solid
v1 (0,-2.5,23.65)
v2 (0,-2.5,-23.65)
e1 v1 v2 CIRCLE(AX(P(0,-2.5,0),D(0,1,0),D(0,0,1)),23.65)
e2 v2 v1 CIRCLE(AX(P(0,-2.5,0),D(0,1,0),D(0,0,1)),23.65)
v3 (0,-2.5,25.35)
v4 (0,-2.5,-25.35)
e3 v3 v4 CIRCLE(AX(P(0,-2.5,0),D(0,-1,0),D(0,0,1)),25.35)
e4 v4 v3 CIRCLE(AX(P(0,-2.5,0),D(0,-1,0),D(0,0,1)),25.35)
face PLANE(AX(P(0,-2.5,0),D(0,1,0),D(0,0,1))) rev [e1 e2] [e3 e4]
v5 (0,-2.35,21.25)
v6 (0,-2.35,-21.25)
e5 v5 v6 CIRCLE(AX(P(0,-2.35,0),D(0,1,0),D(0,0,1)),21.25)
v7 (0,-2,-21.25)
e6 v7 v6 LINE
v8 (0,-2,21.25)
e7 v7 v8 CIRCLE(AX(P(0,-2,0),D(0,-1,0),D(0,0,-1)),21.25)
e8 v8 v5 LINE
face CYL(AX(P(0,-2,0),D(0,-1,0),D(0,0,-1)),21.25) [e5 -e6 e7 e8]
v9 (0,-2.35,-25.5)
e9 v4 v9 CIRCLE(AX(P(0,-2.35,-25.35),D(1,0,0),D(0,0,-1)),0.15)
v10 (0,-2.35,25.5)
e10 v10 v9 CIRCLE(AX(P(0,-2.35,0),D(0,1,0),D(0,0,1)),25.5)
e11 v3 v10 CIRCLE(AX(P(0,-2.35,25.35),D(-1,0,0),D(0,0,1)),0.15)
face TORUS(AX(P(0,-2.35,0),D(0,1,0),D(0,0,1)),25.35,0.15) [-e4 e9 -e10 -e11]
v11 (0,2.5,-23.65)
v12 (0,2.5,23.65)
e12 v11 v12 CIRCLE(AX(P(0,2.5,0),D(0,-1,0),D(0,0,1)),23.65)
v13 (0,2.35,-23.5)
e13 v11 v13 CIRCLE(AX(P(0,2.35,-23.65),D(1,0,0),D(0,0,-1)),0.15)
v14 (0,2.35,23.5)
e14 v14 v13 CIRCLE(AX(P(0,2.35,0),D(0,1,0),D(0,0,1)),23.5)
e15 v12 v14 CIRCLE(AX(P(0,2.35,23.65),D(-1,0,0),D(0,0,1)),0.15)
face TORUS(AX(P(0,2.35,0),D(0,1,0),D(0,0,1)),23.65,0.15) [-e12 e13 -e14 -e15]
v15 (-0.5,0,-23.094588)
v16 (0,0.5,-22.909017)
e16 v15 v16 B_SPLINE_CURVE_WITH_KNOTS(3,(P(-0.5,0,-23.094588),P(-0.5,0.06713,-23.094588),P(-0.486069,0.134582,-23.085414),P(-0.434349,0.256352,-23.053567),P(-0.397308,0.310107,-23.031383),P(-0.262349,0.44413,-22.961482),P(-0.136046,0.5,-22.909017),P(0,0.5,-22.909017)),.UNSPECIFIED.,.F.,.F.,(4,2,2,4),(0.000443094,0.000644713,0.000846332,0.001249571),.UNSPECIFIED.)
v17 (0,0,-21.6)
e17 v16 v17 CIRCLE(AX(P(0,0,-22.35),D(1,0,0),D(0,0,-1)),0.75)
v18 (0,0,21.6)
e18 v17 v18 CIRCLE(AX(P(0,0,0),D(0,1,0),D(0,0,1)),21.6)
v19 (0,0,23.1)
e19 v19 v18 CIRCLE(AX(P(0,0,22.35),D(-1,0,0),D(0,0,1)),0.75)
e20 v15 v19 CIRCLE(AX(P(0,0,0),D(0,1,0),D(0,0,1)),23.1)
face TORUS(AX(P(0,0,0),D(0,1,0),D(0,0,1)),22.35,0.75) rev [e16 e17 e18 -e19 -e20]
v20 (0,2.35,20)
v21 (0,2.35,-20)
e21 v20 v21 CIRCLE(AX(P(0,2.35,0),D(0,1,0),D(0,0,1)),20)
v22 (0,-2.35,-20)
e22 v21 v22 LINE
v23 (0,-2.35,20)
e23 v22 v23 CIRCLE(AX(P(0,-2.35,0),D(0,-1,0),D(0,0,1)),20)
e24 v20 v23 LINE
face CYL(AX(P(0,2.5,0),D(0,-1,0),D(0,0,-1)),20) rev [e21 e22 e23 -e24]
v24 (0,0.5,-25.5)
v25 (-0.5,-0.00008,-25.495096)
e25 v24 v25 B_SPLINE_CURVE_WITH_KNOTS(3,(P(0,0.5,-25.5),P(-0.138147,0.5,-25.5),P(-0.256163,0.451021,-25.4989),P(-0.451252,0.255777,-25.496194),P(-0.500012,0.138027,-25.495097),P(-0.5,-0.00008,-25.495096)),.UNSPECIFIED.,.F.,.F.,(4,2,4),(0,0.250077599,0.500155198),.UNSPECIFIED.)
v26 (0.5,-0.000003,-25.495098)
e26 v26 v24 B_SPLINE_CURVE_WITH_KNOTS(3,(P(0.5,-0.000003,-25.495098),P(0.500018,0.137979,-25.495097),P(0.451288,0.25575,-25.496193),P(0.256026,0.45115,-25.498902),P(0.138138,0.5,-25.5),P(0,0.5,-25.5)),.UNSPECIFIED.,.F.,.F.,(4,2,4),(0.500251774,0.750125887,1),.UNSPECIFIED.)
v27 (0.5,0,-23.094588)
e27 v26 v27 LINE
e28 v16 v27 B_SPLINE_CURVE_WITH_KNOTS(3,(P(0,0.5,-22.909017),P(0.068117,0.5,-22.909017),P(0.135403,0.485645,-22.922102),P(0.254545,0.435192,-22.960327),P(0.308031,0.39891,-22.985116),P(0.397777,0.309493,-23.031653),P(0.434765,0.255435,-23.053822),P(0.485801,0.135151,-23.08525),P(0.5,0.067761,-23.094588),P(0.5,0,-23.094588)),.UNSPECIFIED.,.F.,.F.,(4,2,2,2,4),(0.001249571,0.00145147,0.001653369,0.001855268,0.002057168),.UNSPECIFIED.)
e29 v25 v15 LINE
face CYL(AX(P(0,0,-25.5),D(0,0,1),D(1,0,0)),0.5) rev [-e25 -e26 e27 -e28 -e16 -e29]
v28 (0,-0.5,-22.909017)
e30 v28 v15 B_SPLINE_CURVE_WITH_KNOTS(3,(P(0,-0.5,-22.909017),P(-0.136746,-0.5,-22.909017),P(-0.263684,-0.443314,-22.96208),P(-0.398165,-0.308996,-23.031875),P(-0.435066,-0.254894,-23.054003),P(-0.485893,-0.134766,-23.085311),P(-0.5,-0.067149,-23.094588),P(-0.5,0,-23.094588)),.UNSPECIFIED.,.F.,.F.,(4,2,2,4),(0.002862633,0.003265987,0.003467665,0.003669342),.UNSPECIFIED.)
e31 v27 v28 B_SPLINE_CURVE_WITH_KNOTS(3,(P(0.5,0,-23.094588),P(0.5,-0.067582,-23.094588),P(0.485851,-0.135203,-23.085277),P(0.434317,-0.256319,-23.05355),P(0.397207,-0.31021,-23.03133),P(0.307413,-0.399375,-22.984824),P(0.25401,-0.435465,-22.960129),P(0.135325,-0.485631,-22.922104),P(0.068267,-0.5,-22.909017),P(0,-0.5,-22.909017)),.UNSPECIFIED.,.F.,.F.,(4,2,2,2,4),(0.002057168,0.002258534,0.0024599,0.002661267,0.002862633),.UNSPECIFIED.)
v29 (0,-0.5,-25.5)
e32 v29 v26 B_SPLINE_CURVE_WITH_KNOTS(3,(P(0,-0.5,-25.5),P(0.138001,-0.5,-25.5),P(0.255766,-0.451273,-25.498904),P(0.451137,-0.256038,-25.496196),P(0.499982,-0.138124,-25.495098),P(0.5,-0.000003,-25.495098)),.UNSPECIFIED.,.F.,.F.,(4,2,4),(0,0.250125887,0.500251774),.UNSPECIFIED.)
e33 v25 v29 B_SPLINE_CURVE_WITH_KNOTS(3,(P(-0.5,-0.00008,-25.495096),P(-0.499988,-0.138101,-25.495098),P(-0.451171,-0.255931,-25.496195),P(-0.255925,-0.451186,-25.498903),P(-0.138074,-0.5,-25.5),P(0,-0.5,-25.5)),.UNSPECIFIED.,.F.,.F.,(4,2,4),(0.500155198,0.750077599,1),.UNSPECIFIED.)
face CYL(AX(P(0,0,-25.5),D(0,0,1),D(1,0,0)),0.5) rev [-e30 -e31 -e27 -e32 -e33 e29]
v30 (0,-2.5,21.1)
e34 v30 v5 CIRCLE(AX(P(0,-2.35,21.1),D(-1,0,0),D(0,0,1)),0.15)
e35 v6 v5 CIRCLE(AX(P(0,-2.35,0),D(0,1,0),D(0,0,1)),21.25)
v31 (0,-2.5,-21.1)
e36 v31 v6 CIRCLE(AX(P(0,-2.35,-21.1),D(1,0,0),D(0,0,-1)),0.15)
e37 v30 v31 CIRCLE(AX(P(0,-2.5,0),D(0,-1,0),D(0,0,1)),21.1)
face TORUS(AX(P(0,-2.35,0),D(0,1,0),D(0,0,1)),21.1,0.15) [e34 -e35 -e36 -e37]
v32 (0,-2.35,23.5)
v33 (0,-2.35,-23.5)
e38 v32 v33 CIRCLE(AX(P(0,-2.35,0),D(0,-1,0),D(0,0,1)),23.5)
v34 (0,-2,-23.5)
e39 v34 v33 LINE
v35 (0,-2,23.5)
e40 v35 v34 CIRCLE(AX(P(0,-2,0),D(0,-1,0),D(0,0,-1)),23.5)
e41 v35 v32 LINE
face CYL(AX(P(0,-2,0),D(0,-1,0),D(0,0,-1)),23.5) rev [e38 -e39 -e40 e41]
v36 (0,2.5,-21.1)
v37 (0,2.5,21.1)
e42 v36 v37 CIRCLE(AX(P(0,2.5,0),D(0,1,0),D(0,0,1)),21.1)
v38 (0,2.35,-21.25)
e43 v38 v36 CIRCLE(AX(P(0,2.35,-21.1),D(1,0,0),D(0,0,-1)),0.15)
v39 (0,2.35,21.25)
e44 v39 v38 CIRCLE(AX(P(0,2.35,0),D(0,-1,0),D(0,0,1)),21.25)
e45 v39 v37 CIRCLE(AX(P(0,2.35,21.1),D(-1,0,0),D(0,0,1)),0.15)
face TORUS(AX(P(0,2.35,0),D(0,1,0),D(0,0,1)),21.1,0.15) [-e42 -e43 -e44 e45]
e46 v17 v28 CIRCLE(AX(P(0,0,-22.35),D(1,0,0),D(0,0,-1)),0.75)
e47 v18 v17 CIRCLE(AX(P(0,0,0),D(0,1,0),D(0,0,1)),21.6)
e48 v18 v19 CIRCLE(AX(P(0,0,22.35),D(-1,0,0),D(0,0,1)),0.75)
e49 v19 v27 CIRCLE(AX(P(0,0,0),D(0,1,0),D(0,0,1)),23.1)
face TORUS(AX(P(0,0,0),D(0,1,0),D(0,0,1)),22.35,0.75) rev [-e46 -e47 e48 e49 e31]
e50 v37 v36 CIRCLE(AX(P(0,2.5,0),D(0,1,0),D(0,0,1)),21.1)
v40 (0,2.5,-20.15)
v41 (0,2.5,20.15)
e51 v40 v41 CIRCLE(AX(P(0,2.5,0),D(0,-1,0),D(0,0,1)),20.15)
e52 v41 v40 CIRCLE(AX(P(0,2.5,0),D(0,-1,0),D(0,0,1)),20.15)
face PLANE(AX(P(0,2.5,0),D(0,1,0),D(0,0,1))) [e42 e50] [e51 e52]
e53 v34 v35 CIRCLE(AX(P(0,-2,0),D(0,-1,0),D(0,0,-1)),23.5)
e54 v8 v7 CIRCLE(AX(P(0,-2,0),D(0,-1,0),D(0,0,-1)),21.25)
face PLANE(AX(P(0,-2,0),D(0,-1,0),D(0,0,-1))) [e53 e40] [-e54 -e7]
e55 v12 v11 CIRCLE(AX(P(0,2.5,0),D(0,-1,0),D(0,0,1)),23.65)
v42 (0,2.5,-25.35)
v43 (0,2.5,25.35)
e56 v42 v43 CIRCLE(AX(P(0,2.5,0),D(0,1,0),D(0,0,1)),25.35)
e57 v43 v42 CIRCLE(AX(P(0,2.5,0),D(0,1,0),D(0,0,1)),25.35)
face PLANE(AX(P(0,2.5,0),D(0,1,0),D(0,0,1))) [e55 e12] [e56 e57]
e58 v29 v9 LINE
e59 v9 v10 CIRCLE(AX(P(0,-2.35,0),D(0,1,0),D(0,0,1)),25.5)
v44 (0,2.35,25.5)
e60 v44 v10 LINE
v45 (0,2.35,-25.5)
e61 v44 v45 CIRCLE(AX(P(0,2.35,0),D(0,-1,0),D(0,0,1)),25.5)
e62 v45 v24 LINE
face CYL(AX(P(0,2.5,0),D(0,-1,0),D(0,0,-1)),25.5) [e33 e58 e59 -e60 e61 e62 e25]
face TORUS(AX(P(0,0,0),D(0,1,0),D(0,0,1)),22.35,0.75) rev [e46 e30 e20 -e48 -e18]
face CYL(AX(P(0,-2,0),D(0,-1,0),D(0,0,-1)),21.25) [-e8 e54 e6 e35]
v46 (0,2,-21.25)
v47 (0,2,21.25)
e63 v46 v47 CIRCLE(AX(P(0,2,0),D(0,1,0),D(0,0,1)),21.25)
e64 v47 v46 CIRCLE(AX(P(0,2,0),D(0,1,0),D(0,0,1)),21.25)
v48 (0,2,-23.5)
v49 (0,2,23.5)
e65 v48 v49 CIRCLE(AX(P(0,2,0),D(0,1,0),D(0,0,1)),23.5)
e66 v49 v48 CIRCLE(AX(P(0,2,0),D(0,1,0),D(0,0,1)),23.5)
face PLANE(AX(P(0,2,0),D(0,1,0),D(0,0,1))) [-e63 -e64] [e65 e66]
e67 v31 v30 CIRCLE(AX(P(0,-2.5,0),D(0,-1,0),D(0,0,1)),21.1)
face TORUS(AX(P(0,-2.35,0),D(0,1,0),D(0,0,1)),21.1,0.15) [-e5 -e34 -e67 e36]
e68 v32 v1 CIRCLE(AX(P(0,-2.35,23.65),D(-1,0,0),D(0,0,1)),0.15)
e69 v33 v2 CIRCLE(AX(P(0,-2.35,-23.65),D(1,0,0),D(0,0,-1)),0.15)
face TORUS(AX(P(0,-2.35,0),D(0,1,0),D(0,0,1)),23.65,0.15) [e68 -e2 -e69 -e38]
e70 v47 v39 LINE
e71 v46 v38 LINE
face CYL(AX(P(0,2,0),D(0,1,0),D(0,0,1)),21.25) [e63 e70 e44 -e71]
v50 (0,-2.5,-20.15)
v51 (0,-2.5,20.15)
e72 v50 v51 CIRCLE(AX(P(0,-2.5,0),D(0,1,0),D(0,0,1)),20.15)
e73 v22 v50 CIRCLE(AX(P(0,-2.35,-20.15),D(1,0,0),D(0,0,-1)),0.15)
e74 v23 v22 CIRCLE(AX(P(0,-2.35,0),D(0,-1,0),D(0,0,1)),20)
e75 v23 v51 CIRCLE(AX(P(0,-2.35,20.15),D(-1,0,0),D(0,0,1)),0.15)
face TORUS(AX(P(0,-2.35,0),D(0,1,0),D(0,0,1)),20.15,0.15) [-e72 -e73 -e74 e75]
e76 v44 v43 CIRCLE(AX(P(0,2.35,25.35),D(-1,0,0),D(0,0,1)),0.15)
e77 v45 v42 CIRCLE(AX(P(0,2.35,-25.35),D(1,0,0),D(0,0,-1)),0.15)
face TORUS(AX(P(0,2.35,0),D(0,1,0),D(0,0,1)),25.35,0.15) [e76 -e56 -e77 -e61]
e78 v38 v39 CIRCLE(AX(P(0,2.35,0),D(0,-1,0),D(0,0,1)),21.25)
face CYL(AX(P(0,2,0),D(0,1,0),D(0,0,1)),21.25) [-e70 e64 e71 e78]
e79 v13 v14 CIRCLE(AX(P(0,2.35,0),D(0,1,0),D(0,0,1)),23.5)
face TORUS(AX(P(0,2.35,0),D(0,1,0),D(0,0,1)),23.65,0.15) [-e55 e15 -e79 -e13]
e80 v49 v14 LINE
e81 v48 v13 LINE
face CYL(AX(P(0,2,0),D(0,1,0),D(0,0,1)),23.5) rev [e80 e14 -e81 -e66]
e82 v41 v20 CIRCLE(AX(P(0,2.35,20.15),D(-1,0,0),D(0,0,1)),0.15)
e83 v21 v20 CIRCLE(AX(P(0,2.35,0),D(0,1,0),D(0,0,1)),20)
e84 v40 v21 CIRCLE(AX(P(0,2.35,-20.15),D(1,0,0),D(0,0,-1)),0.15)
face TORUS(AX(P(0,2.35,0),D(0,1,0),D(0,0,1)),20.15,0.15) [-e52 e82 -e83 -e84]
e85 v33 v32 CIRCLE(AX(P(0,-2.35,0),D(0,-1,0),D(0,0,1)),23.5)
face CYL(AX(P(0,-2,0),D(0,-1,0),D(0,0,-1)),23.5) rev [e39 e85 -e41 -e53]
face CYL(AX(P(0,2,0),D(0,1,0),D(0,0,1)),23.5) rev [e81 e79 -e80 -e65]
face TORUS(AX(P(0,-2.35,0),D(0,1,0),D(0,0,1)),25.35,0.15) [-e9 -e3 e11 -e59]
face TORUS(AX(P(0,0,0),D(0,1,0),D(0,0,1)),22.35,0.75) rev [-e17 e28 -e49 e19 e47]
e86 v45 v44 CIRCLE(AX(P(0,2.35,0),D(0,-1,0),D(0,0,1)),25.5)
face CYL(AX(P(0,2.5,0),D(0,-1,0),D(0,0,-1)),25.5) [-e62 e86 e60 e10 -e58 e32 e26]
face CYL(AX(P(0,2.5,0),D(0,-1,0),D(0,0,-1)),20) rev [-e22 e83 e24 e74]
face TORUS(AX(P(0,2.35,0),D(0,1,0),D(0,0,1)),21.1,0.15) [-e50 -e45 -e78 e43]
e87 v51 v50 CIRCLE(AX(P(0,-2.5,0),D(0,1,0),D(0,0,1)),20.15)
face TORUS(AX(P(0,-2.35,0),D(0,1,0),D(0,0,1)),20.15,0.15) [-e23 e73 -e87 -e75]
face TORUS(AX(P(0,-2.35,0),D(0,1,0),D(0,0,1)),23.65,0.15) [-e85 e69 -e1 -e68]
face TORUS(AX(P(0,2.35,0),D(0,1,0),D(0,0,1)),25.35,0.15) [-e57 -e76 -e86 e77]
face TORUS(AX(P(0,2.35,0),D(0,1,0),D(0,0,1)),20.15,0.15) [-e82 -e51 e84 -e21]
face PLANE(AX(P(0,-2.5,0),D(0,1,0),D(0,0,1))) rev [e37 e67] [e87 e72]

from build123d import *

# Parameters (mm, degrees)
SKETCH_1_R            = 25.5
SKETCH_1_R_2          = 20
EXTRUDE_1_DEPTH       = 2.5
SKETCH_2_R            = 23.5
SKETCH_2_R_2          = 21.25
CUT_EXTRUDE_433_DEPTH = 0.5
CUT_EXTRUDE_START     = -0.5
SKETCH_3_R            = 23.5
SKETCH_3_R_2          = 21.25
CUT_EXTRUDE_567_DEPTH = 0.5
SKETCH_4_R            = 0.75
CUT_EXTRUDE_START_2   = -22.35
SKETCH_5_R            = 0.5
CUT_EXTRUDE_1_DEPTH   = 14.79899722
FILLET_R0_15_R        = 0.15


with BuildPart() as part:
    # 草图1 → 凸台-拉伸1 (new, symmetric)
    with BuildSketch(Plane(origin=(0, 0, 0), x_dir=(1, 0, 0), z_dir=(0, 1, 0))):
        with Locations(Location((0, 0, 0), (0, 0, 270))):
            Circle(SKETCH_1_R)
        with Locations(Location((0, 0, 0), (0, 0, 270))):
            Circle(SKETCH_1_R_2, mode=Mode.SUBTRACT)
    extrude(amount=EXTRUDE_1_DEPTH, both=True)

    # 草图2 → Cut-Extrude 433 (cut)
    with BuildSketch(Plane(origin=(0, 2.5, 0), x_dir=(1, 0, 0), z_dir=(0, 1, 0))):
        with Locations(Location((0, 0, 0), (0, 0, 270))):
            Circle(SKETCH_2_R)
        with Locations(Location((0, 0, 0), (0, 0, 270))):
            Circle(SKETCH_2_R_2, mode=Mode.SUBTRACT)
    extrude(amount=-CUT_EXTRUDE_433_DEPTH, mode=Mode.SUBTRACT)

    # 草图3 → Cut-Extrude 567 (cut)
    with BuildSketch(Plane.XZ.offset(2.5).offset(CUT_EXTRUDE_START)):
        with Locations(Location((0, 0, 0), (0, 0, 90))):
            Circle(SKETCH_3_R)
        with Locations(Location((0, 0, 0), (0, 0, 90))):
            Circle(SKETCH_3_R_2, mode=Mode.SUBTRACT)
    extrude(amount=CUT_EXTRUDE_567_DEPTH, mode=Mode.SUBTRACT)

    # 草图4 → Cut-Revolve 663 (revolve, cut)
    with BuildSketch(Plane.XY, mode=Mode.PRIVATE) as cut_revolve_663_sk:
        with Locations((-22.35, 0)):
            Circle(SKETCH_4_R)
    revolve(cut_revolve_663_sk.sketch.rotate(Axis((0, 2.5, 0), (0, -1, 0)), 90), axis=Axis((0, 2.5, 0), (0, -1, 0)), mode=Mode.SUBTRACT)

    # 草图5 → 切除-拉伸1 (cut, through all)
    with BuildSketch(Plane.XY.offset(CUT_EXTRUDE_START_2)):
        with Locations(Location((0, 0, 0), (0, 0, 270))):
            Circle(SKETCH_5_R)
    extrude(amount=-CUT_EXTRUDE_1_DEPTH, mode=Mode.SUBTRACT)

    # R0.15 圆角
    fillet_r0_15_edges = [part.edges().sort_by_distance(p)[0] for p in [
        (0, 2.5, -23.5),
        (0, 2.5, -21.25),
        (0, -2.5, -23.5),
        (0, -2.5, -25.5),
        (0, -2.5, -21.25),
        (0, 2.5, -25.5),
        (0, -2.5, -20),
        (0, 2.5, -20),
    ]]
    fillet(fillet_r0_15_edges, radius=FILLET_R0_15_R)


solid = part.part
